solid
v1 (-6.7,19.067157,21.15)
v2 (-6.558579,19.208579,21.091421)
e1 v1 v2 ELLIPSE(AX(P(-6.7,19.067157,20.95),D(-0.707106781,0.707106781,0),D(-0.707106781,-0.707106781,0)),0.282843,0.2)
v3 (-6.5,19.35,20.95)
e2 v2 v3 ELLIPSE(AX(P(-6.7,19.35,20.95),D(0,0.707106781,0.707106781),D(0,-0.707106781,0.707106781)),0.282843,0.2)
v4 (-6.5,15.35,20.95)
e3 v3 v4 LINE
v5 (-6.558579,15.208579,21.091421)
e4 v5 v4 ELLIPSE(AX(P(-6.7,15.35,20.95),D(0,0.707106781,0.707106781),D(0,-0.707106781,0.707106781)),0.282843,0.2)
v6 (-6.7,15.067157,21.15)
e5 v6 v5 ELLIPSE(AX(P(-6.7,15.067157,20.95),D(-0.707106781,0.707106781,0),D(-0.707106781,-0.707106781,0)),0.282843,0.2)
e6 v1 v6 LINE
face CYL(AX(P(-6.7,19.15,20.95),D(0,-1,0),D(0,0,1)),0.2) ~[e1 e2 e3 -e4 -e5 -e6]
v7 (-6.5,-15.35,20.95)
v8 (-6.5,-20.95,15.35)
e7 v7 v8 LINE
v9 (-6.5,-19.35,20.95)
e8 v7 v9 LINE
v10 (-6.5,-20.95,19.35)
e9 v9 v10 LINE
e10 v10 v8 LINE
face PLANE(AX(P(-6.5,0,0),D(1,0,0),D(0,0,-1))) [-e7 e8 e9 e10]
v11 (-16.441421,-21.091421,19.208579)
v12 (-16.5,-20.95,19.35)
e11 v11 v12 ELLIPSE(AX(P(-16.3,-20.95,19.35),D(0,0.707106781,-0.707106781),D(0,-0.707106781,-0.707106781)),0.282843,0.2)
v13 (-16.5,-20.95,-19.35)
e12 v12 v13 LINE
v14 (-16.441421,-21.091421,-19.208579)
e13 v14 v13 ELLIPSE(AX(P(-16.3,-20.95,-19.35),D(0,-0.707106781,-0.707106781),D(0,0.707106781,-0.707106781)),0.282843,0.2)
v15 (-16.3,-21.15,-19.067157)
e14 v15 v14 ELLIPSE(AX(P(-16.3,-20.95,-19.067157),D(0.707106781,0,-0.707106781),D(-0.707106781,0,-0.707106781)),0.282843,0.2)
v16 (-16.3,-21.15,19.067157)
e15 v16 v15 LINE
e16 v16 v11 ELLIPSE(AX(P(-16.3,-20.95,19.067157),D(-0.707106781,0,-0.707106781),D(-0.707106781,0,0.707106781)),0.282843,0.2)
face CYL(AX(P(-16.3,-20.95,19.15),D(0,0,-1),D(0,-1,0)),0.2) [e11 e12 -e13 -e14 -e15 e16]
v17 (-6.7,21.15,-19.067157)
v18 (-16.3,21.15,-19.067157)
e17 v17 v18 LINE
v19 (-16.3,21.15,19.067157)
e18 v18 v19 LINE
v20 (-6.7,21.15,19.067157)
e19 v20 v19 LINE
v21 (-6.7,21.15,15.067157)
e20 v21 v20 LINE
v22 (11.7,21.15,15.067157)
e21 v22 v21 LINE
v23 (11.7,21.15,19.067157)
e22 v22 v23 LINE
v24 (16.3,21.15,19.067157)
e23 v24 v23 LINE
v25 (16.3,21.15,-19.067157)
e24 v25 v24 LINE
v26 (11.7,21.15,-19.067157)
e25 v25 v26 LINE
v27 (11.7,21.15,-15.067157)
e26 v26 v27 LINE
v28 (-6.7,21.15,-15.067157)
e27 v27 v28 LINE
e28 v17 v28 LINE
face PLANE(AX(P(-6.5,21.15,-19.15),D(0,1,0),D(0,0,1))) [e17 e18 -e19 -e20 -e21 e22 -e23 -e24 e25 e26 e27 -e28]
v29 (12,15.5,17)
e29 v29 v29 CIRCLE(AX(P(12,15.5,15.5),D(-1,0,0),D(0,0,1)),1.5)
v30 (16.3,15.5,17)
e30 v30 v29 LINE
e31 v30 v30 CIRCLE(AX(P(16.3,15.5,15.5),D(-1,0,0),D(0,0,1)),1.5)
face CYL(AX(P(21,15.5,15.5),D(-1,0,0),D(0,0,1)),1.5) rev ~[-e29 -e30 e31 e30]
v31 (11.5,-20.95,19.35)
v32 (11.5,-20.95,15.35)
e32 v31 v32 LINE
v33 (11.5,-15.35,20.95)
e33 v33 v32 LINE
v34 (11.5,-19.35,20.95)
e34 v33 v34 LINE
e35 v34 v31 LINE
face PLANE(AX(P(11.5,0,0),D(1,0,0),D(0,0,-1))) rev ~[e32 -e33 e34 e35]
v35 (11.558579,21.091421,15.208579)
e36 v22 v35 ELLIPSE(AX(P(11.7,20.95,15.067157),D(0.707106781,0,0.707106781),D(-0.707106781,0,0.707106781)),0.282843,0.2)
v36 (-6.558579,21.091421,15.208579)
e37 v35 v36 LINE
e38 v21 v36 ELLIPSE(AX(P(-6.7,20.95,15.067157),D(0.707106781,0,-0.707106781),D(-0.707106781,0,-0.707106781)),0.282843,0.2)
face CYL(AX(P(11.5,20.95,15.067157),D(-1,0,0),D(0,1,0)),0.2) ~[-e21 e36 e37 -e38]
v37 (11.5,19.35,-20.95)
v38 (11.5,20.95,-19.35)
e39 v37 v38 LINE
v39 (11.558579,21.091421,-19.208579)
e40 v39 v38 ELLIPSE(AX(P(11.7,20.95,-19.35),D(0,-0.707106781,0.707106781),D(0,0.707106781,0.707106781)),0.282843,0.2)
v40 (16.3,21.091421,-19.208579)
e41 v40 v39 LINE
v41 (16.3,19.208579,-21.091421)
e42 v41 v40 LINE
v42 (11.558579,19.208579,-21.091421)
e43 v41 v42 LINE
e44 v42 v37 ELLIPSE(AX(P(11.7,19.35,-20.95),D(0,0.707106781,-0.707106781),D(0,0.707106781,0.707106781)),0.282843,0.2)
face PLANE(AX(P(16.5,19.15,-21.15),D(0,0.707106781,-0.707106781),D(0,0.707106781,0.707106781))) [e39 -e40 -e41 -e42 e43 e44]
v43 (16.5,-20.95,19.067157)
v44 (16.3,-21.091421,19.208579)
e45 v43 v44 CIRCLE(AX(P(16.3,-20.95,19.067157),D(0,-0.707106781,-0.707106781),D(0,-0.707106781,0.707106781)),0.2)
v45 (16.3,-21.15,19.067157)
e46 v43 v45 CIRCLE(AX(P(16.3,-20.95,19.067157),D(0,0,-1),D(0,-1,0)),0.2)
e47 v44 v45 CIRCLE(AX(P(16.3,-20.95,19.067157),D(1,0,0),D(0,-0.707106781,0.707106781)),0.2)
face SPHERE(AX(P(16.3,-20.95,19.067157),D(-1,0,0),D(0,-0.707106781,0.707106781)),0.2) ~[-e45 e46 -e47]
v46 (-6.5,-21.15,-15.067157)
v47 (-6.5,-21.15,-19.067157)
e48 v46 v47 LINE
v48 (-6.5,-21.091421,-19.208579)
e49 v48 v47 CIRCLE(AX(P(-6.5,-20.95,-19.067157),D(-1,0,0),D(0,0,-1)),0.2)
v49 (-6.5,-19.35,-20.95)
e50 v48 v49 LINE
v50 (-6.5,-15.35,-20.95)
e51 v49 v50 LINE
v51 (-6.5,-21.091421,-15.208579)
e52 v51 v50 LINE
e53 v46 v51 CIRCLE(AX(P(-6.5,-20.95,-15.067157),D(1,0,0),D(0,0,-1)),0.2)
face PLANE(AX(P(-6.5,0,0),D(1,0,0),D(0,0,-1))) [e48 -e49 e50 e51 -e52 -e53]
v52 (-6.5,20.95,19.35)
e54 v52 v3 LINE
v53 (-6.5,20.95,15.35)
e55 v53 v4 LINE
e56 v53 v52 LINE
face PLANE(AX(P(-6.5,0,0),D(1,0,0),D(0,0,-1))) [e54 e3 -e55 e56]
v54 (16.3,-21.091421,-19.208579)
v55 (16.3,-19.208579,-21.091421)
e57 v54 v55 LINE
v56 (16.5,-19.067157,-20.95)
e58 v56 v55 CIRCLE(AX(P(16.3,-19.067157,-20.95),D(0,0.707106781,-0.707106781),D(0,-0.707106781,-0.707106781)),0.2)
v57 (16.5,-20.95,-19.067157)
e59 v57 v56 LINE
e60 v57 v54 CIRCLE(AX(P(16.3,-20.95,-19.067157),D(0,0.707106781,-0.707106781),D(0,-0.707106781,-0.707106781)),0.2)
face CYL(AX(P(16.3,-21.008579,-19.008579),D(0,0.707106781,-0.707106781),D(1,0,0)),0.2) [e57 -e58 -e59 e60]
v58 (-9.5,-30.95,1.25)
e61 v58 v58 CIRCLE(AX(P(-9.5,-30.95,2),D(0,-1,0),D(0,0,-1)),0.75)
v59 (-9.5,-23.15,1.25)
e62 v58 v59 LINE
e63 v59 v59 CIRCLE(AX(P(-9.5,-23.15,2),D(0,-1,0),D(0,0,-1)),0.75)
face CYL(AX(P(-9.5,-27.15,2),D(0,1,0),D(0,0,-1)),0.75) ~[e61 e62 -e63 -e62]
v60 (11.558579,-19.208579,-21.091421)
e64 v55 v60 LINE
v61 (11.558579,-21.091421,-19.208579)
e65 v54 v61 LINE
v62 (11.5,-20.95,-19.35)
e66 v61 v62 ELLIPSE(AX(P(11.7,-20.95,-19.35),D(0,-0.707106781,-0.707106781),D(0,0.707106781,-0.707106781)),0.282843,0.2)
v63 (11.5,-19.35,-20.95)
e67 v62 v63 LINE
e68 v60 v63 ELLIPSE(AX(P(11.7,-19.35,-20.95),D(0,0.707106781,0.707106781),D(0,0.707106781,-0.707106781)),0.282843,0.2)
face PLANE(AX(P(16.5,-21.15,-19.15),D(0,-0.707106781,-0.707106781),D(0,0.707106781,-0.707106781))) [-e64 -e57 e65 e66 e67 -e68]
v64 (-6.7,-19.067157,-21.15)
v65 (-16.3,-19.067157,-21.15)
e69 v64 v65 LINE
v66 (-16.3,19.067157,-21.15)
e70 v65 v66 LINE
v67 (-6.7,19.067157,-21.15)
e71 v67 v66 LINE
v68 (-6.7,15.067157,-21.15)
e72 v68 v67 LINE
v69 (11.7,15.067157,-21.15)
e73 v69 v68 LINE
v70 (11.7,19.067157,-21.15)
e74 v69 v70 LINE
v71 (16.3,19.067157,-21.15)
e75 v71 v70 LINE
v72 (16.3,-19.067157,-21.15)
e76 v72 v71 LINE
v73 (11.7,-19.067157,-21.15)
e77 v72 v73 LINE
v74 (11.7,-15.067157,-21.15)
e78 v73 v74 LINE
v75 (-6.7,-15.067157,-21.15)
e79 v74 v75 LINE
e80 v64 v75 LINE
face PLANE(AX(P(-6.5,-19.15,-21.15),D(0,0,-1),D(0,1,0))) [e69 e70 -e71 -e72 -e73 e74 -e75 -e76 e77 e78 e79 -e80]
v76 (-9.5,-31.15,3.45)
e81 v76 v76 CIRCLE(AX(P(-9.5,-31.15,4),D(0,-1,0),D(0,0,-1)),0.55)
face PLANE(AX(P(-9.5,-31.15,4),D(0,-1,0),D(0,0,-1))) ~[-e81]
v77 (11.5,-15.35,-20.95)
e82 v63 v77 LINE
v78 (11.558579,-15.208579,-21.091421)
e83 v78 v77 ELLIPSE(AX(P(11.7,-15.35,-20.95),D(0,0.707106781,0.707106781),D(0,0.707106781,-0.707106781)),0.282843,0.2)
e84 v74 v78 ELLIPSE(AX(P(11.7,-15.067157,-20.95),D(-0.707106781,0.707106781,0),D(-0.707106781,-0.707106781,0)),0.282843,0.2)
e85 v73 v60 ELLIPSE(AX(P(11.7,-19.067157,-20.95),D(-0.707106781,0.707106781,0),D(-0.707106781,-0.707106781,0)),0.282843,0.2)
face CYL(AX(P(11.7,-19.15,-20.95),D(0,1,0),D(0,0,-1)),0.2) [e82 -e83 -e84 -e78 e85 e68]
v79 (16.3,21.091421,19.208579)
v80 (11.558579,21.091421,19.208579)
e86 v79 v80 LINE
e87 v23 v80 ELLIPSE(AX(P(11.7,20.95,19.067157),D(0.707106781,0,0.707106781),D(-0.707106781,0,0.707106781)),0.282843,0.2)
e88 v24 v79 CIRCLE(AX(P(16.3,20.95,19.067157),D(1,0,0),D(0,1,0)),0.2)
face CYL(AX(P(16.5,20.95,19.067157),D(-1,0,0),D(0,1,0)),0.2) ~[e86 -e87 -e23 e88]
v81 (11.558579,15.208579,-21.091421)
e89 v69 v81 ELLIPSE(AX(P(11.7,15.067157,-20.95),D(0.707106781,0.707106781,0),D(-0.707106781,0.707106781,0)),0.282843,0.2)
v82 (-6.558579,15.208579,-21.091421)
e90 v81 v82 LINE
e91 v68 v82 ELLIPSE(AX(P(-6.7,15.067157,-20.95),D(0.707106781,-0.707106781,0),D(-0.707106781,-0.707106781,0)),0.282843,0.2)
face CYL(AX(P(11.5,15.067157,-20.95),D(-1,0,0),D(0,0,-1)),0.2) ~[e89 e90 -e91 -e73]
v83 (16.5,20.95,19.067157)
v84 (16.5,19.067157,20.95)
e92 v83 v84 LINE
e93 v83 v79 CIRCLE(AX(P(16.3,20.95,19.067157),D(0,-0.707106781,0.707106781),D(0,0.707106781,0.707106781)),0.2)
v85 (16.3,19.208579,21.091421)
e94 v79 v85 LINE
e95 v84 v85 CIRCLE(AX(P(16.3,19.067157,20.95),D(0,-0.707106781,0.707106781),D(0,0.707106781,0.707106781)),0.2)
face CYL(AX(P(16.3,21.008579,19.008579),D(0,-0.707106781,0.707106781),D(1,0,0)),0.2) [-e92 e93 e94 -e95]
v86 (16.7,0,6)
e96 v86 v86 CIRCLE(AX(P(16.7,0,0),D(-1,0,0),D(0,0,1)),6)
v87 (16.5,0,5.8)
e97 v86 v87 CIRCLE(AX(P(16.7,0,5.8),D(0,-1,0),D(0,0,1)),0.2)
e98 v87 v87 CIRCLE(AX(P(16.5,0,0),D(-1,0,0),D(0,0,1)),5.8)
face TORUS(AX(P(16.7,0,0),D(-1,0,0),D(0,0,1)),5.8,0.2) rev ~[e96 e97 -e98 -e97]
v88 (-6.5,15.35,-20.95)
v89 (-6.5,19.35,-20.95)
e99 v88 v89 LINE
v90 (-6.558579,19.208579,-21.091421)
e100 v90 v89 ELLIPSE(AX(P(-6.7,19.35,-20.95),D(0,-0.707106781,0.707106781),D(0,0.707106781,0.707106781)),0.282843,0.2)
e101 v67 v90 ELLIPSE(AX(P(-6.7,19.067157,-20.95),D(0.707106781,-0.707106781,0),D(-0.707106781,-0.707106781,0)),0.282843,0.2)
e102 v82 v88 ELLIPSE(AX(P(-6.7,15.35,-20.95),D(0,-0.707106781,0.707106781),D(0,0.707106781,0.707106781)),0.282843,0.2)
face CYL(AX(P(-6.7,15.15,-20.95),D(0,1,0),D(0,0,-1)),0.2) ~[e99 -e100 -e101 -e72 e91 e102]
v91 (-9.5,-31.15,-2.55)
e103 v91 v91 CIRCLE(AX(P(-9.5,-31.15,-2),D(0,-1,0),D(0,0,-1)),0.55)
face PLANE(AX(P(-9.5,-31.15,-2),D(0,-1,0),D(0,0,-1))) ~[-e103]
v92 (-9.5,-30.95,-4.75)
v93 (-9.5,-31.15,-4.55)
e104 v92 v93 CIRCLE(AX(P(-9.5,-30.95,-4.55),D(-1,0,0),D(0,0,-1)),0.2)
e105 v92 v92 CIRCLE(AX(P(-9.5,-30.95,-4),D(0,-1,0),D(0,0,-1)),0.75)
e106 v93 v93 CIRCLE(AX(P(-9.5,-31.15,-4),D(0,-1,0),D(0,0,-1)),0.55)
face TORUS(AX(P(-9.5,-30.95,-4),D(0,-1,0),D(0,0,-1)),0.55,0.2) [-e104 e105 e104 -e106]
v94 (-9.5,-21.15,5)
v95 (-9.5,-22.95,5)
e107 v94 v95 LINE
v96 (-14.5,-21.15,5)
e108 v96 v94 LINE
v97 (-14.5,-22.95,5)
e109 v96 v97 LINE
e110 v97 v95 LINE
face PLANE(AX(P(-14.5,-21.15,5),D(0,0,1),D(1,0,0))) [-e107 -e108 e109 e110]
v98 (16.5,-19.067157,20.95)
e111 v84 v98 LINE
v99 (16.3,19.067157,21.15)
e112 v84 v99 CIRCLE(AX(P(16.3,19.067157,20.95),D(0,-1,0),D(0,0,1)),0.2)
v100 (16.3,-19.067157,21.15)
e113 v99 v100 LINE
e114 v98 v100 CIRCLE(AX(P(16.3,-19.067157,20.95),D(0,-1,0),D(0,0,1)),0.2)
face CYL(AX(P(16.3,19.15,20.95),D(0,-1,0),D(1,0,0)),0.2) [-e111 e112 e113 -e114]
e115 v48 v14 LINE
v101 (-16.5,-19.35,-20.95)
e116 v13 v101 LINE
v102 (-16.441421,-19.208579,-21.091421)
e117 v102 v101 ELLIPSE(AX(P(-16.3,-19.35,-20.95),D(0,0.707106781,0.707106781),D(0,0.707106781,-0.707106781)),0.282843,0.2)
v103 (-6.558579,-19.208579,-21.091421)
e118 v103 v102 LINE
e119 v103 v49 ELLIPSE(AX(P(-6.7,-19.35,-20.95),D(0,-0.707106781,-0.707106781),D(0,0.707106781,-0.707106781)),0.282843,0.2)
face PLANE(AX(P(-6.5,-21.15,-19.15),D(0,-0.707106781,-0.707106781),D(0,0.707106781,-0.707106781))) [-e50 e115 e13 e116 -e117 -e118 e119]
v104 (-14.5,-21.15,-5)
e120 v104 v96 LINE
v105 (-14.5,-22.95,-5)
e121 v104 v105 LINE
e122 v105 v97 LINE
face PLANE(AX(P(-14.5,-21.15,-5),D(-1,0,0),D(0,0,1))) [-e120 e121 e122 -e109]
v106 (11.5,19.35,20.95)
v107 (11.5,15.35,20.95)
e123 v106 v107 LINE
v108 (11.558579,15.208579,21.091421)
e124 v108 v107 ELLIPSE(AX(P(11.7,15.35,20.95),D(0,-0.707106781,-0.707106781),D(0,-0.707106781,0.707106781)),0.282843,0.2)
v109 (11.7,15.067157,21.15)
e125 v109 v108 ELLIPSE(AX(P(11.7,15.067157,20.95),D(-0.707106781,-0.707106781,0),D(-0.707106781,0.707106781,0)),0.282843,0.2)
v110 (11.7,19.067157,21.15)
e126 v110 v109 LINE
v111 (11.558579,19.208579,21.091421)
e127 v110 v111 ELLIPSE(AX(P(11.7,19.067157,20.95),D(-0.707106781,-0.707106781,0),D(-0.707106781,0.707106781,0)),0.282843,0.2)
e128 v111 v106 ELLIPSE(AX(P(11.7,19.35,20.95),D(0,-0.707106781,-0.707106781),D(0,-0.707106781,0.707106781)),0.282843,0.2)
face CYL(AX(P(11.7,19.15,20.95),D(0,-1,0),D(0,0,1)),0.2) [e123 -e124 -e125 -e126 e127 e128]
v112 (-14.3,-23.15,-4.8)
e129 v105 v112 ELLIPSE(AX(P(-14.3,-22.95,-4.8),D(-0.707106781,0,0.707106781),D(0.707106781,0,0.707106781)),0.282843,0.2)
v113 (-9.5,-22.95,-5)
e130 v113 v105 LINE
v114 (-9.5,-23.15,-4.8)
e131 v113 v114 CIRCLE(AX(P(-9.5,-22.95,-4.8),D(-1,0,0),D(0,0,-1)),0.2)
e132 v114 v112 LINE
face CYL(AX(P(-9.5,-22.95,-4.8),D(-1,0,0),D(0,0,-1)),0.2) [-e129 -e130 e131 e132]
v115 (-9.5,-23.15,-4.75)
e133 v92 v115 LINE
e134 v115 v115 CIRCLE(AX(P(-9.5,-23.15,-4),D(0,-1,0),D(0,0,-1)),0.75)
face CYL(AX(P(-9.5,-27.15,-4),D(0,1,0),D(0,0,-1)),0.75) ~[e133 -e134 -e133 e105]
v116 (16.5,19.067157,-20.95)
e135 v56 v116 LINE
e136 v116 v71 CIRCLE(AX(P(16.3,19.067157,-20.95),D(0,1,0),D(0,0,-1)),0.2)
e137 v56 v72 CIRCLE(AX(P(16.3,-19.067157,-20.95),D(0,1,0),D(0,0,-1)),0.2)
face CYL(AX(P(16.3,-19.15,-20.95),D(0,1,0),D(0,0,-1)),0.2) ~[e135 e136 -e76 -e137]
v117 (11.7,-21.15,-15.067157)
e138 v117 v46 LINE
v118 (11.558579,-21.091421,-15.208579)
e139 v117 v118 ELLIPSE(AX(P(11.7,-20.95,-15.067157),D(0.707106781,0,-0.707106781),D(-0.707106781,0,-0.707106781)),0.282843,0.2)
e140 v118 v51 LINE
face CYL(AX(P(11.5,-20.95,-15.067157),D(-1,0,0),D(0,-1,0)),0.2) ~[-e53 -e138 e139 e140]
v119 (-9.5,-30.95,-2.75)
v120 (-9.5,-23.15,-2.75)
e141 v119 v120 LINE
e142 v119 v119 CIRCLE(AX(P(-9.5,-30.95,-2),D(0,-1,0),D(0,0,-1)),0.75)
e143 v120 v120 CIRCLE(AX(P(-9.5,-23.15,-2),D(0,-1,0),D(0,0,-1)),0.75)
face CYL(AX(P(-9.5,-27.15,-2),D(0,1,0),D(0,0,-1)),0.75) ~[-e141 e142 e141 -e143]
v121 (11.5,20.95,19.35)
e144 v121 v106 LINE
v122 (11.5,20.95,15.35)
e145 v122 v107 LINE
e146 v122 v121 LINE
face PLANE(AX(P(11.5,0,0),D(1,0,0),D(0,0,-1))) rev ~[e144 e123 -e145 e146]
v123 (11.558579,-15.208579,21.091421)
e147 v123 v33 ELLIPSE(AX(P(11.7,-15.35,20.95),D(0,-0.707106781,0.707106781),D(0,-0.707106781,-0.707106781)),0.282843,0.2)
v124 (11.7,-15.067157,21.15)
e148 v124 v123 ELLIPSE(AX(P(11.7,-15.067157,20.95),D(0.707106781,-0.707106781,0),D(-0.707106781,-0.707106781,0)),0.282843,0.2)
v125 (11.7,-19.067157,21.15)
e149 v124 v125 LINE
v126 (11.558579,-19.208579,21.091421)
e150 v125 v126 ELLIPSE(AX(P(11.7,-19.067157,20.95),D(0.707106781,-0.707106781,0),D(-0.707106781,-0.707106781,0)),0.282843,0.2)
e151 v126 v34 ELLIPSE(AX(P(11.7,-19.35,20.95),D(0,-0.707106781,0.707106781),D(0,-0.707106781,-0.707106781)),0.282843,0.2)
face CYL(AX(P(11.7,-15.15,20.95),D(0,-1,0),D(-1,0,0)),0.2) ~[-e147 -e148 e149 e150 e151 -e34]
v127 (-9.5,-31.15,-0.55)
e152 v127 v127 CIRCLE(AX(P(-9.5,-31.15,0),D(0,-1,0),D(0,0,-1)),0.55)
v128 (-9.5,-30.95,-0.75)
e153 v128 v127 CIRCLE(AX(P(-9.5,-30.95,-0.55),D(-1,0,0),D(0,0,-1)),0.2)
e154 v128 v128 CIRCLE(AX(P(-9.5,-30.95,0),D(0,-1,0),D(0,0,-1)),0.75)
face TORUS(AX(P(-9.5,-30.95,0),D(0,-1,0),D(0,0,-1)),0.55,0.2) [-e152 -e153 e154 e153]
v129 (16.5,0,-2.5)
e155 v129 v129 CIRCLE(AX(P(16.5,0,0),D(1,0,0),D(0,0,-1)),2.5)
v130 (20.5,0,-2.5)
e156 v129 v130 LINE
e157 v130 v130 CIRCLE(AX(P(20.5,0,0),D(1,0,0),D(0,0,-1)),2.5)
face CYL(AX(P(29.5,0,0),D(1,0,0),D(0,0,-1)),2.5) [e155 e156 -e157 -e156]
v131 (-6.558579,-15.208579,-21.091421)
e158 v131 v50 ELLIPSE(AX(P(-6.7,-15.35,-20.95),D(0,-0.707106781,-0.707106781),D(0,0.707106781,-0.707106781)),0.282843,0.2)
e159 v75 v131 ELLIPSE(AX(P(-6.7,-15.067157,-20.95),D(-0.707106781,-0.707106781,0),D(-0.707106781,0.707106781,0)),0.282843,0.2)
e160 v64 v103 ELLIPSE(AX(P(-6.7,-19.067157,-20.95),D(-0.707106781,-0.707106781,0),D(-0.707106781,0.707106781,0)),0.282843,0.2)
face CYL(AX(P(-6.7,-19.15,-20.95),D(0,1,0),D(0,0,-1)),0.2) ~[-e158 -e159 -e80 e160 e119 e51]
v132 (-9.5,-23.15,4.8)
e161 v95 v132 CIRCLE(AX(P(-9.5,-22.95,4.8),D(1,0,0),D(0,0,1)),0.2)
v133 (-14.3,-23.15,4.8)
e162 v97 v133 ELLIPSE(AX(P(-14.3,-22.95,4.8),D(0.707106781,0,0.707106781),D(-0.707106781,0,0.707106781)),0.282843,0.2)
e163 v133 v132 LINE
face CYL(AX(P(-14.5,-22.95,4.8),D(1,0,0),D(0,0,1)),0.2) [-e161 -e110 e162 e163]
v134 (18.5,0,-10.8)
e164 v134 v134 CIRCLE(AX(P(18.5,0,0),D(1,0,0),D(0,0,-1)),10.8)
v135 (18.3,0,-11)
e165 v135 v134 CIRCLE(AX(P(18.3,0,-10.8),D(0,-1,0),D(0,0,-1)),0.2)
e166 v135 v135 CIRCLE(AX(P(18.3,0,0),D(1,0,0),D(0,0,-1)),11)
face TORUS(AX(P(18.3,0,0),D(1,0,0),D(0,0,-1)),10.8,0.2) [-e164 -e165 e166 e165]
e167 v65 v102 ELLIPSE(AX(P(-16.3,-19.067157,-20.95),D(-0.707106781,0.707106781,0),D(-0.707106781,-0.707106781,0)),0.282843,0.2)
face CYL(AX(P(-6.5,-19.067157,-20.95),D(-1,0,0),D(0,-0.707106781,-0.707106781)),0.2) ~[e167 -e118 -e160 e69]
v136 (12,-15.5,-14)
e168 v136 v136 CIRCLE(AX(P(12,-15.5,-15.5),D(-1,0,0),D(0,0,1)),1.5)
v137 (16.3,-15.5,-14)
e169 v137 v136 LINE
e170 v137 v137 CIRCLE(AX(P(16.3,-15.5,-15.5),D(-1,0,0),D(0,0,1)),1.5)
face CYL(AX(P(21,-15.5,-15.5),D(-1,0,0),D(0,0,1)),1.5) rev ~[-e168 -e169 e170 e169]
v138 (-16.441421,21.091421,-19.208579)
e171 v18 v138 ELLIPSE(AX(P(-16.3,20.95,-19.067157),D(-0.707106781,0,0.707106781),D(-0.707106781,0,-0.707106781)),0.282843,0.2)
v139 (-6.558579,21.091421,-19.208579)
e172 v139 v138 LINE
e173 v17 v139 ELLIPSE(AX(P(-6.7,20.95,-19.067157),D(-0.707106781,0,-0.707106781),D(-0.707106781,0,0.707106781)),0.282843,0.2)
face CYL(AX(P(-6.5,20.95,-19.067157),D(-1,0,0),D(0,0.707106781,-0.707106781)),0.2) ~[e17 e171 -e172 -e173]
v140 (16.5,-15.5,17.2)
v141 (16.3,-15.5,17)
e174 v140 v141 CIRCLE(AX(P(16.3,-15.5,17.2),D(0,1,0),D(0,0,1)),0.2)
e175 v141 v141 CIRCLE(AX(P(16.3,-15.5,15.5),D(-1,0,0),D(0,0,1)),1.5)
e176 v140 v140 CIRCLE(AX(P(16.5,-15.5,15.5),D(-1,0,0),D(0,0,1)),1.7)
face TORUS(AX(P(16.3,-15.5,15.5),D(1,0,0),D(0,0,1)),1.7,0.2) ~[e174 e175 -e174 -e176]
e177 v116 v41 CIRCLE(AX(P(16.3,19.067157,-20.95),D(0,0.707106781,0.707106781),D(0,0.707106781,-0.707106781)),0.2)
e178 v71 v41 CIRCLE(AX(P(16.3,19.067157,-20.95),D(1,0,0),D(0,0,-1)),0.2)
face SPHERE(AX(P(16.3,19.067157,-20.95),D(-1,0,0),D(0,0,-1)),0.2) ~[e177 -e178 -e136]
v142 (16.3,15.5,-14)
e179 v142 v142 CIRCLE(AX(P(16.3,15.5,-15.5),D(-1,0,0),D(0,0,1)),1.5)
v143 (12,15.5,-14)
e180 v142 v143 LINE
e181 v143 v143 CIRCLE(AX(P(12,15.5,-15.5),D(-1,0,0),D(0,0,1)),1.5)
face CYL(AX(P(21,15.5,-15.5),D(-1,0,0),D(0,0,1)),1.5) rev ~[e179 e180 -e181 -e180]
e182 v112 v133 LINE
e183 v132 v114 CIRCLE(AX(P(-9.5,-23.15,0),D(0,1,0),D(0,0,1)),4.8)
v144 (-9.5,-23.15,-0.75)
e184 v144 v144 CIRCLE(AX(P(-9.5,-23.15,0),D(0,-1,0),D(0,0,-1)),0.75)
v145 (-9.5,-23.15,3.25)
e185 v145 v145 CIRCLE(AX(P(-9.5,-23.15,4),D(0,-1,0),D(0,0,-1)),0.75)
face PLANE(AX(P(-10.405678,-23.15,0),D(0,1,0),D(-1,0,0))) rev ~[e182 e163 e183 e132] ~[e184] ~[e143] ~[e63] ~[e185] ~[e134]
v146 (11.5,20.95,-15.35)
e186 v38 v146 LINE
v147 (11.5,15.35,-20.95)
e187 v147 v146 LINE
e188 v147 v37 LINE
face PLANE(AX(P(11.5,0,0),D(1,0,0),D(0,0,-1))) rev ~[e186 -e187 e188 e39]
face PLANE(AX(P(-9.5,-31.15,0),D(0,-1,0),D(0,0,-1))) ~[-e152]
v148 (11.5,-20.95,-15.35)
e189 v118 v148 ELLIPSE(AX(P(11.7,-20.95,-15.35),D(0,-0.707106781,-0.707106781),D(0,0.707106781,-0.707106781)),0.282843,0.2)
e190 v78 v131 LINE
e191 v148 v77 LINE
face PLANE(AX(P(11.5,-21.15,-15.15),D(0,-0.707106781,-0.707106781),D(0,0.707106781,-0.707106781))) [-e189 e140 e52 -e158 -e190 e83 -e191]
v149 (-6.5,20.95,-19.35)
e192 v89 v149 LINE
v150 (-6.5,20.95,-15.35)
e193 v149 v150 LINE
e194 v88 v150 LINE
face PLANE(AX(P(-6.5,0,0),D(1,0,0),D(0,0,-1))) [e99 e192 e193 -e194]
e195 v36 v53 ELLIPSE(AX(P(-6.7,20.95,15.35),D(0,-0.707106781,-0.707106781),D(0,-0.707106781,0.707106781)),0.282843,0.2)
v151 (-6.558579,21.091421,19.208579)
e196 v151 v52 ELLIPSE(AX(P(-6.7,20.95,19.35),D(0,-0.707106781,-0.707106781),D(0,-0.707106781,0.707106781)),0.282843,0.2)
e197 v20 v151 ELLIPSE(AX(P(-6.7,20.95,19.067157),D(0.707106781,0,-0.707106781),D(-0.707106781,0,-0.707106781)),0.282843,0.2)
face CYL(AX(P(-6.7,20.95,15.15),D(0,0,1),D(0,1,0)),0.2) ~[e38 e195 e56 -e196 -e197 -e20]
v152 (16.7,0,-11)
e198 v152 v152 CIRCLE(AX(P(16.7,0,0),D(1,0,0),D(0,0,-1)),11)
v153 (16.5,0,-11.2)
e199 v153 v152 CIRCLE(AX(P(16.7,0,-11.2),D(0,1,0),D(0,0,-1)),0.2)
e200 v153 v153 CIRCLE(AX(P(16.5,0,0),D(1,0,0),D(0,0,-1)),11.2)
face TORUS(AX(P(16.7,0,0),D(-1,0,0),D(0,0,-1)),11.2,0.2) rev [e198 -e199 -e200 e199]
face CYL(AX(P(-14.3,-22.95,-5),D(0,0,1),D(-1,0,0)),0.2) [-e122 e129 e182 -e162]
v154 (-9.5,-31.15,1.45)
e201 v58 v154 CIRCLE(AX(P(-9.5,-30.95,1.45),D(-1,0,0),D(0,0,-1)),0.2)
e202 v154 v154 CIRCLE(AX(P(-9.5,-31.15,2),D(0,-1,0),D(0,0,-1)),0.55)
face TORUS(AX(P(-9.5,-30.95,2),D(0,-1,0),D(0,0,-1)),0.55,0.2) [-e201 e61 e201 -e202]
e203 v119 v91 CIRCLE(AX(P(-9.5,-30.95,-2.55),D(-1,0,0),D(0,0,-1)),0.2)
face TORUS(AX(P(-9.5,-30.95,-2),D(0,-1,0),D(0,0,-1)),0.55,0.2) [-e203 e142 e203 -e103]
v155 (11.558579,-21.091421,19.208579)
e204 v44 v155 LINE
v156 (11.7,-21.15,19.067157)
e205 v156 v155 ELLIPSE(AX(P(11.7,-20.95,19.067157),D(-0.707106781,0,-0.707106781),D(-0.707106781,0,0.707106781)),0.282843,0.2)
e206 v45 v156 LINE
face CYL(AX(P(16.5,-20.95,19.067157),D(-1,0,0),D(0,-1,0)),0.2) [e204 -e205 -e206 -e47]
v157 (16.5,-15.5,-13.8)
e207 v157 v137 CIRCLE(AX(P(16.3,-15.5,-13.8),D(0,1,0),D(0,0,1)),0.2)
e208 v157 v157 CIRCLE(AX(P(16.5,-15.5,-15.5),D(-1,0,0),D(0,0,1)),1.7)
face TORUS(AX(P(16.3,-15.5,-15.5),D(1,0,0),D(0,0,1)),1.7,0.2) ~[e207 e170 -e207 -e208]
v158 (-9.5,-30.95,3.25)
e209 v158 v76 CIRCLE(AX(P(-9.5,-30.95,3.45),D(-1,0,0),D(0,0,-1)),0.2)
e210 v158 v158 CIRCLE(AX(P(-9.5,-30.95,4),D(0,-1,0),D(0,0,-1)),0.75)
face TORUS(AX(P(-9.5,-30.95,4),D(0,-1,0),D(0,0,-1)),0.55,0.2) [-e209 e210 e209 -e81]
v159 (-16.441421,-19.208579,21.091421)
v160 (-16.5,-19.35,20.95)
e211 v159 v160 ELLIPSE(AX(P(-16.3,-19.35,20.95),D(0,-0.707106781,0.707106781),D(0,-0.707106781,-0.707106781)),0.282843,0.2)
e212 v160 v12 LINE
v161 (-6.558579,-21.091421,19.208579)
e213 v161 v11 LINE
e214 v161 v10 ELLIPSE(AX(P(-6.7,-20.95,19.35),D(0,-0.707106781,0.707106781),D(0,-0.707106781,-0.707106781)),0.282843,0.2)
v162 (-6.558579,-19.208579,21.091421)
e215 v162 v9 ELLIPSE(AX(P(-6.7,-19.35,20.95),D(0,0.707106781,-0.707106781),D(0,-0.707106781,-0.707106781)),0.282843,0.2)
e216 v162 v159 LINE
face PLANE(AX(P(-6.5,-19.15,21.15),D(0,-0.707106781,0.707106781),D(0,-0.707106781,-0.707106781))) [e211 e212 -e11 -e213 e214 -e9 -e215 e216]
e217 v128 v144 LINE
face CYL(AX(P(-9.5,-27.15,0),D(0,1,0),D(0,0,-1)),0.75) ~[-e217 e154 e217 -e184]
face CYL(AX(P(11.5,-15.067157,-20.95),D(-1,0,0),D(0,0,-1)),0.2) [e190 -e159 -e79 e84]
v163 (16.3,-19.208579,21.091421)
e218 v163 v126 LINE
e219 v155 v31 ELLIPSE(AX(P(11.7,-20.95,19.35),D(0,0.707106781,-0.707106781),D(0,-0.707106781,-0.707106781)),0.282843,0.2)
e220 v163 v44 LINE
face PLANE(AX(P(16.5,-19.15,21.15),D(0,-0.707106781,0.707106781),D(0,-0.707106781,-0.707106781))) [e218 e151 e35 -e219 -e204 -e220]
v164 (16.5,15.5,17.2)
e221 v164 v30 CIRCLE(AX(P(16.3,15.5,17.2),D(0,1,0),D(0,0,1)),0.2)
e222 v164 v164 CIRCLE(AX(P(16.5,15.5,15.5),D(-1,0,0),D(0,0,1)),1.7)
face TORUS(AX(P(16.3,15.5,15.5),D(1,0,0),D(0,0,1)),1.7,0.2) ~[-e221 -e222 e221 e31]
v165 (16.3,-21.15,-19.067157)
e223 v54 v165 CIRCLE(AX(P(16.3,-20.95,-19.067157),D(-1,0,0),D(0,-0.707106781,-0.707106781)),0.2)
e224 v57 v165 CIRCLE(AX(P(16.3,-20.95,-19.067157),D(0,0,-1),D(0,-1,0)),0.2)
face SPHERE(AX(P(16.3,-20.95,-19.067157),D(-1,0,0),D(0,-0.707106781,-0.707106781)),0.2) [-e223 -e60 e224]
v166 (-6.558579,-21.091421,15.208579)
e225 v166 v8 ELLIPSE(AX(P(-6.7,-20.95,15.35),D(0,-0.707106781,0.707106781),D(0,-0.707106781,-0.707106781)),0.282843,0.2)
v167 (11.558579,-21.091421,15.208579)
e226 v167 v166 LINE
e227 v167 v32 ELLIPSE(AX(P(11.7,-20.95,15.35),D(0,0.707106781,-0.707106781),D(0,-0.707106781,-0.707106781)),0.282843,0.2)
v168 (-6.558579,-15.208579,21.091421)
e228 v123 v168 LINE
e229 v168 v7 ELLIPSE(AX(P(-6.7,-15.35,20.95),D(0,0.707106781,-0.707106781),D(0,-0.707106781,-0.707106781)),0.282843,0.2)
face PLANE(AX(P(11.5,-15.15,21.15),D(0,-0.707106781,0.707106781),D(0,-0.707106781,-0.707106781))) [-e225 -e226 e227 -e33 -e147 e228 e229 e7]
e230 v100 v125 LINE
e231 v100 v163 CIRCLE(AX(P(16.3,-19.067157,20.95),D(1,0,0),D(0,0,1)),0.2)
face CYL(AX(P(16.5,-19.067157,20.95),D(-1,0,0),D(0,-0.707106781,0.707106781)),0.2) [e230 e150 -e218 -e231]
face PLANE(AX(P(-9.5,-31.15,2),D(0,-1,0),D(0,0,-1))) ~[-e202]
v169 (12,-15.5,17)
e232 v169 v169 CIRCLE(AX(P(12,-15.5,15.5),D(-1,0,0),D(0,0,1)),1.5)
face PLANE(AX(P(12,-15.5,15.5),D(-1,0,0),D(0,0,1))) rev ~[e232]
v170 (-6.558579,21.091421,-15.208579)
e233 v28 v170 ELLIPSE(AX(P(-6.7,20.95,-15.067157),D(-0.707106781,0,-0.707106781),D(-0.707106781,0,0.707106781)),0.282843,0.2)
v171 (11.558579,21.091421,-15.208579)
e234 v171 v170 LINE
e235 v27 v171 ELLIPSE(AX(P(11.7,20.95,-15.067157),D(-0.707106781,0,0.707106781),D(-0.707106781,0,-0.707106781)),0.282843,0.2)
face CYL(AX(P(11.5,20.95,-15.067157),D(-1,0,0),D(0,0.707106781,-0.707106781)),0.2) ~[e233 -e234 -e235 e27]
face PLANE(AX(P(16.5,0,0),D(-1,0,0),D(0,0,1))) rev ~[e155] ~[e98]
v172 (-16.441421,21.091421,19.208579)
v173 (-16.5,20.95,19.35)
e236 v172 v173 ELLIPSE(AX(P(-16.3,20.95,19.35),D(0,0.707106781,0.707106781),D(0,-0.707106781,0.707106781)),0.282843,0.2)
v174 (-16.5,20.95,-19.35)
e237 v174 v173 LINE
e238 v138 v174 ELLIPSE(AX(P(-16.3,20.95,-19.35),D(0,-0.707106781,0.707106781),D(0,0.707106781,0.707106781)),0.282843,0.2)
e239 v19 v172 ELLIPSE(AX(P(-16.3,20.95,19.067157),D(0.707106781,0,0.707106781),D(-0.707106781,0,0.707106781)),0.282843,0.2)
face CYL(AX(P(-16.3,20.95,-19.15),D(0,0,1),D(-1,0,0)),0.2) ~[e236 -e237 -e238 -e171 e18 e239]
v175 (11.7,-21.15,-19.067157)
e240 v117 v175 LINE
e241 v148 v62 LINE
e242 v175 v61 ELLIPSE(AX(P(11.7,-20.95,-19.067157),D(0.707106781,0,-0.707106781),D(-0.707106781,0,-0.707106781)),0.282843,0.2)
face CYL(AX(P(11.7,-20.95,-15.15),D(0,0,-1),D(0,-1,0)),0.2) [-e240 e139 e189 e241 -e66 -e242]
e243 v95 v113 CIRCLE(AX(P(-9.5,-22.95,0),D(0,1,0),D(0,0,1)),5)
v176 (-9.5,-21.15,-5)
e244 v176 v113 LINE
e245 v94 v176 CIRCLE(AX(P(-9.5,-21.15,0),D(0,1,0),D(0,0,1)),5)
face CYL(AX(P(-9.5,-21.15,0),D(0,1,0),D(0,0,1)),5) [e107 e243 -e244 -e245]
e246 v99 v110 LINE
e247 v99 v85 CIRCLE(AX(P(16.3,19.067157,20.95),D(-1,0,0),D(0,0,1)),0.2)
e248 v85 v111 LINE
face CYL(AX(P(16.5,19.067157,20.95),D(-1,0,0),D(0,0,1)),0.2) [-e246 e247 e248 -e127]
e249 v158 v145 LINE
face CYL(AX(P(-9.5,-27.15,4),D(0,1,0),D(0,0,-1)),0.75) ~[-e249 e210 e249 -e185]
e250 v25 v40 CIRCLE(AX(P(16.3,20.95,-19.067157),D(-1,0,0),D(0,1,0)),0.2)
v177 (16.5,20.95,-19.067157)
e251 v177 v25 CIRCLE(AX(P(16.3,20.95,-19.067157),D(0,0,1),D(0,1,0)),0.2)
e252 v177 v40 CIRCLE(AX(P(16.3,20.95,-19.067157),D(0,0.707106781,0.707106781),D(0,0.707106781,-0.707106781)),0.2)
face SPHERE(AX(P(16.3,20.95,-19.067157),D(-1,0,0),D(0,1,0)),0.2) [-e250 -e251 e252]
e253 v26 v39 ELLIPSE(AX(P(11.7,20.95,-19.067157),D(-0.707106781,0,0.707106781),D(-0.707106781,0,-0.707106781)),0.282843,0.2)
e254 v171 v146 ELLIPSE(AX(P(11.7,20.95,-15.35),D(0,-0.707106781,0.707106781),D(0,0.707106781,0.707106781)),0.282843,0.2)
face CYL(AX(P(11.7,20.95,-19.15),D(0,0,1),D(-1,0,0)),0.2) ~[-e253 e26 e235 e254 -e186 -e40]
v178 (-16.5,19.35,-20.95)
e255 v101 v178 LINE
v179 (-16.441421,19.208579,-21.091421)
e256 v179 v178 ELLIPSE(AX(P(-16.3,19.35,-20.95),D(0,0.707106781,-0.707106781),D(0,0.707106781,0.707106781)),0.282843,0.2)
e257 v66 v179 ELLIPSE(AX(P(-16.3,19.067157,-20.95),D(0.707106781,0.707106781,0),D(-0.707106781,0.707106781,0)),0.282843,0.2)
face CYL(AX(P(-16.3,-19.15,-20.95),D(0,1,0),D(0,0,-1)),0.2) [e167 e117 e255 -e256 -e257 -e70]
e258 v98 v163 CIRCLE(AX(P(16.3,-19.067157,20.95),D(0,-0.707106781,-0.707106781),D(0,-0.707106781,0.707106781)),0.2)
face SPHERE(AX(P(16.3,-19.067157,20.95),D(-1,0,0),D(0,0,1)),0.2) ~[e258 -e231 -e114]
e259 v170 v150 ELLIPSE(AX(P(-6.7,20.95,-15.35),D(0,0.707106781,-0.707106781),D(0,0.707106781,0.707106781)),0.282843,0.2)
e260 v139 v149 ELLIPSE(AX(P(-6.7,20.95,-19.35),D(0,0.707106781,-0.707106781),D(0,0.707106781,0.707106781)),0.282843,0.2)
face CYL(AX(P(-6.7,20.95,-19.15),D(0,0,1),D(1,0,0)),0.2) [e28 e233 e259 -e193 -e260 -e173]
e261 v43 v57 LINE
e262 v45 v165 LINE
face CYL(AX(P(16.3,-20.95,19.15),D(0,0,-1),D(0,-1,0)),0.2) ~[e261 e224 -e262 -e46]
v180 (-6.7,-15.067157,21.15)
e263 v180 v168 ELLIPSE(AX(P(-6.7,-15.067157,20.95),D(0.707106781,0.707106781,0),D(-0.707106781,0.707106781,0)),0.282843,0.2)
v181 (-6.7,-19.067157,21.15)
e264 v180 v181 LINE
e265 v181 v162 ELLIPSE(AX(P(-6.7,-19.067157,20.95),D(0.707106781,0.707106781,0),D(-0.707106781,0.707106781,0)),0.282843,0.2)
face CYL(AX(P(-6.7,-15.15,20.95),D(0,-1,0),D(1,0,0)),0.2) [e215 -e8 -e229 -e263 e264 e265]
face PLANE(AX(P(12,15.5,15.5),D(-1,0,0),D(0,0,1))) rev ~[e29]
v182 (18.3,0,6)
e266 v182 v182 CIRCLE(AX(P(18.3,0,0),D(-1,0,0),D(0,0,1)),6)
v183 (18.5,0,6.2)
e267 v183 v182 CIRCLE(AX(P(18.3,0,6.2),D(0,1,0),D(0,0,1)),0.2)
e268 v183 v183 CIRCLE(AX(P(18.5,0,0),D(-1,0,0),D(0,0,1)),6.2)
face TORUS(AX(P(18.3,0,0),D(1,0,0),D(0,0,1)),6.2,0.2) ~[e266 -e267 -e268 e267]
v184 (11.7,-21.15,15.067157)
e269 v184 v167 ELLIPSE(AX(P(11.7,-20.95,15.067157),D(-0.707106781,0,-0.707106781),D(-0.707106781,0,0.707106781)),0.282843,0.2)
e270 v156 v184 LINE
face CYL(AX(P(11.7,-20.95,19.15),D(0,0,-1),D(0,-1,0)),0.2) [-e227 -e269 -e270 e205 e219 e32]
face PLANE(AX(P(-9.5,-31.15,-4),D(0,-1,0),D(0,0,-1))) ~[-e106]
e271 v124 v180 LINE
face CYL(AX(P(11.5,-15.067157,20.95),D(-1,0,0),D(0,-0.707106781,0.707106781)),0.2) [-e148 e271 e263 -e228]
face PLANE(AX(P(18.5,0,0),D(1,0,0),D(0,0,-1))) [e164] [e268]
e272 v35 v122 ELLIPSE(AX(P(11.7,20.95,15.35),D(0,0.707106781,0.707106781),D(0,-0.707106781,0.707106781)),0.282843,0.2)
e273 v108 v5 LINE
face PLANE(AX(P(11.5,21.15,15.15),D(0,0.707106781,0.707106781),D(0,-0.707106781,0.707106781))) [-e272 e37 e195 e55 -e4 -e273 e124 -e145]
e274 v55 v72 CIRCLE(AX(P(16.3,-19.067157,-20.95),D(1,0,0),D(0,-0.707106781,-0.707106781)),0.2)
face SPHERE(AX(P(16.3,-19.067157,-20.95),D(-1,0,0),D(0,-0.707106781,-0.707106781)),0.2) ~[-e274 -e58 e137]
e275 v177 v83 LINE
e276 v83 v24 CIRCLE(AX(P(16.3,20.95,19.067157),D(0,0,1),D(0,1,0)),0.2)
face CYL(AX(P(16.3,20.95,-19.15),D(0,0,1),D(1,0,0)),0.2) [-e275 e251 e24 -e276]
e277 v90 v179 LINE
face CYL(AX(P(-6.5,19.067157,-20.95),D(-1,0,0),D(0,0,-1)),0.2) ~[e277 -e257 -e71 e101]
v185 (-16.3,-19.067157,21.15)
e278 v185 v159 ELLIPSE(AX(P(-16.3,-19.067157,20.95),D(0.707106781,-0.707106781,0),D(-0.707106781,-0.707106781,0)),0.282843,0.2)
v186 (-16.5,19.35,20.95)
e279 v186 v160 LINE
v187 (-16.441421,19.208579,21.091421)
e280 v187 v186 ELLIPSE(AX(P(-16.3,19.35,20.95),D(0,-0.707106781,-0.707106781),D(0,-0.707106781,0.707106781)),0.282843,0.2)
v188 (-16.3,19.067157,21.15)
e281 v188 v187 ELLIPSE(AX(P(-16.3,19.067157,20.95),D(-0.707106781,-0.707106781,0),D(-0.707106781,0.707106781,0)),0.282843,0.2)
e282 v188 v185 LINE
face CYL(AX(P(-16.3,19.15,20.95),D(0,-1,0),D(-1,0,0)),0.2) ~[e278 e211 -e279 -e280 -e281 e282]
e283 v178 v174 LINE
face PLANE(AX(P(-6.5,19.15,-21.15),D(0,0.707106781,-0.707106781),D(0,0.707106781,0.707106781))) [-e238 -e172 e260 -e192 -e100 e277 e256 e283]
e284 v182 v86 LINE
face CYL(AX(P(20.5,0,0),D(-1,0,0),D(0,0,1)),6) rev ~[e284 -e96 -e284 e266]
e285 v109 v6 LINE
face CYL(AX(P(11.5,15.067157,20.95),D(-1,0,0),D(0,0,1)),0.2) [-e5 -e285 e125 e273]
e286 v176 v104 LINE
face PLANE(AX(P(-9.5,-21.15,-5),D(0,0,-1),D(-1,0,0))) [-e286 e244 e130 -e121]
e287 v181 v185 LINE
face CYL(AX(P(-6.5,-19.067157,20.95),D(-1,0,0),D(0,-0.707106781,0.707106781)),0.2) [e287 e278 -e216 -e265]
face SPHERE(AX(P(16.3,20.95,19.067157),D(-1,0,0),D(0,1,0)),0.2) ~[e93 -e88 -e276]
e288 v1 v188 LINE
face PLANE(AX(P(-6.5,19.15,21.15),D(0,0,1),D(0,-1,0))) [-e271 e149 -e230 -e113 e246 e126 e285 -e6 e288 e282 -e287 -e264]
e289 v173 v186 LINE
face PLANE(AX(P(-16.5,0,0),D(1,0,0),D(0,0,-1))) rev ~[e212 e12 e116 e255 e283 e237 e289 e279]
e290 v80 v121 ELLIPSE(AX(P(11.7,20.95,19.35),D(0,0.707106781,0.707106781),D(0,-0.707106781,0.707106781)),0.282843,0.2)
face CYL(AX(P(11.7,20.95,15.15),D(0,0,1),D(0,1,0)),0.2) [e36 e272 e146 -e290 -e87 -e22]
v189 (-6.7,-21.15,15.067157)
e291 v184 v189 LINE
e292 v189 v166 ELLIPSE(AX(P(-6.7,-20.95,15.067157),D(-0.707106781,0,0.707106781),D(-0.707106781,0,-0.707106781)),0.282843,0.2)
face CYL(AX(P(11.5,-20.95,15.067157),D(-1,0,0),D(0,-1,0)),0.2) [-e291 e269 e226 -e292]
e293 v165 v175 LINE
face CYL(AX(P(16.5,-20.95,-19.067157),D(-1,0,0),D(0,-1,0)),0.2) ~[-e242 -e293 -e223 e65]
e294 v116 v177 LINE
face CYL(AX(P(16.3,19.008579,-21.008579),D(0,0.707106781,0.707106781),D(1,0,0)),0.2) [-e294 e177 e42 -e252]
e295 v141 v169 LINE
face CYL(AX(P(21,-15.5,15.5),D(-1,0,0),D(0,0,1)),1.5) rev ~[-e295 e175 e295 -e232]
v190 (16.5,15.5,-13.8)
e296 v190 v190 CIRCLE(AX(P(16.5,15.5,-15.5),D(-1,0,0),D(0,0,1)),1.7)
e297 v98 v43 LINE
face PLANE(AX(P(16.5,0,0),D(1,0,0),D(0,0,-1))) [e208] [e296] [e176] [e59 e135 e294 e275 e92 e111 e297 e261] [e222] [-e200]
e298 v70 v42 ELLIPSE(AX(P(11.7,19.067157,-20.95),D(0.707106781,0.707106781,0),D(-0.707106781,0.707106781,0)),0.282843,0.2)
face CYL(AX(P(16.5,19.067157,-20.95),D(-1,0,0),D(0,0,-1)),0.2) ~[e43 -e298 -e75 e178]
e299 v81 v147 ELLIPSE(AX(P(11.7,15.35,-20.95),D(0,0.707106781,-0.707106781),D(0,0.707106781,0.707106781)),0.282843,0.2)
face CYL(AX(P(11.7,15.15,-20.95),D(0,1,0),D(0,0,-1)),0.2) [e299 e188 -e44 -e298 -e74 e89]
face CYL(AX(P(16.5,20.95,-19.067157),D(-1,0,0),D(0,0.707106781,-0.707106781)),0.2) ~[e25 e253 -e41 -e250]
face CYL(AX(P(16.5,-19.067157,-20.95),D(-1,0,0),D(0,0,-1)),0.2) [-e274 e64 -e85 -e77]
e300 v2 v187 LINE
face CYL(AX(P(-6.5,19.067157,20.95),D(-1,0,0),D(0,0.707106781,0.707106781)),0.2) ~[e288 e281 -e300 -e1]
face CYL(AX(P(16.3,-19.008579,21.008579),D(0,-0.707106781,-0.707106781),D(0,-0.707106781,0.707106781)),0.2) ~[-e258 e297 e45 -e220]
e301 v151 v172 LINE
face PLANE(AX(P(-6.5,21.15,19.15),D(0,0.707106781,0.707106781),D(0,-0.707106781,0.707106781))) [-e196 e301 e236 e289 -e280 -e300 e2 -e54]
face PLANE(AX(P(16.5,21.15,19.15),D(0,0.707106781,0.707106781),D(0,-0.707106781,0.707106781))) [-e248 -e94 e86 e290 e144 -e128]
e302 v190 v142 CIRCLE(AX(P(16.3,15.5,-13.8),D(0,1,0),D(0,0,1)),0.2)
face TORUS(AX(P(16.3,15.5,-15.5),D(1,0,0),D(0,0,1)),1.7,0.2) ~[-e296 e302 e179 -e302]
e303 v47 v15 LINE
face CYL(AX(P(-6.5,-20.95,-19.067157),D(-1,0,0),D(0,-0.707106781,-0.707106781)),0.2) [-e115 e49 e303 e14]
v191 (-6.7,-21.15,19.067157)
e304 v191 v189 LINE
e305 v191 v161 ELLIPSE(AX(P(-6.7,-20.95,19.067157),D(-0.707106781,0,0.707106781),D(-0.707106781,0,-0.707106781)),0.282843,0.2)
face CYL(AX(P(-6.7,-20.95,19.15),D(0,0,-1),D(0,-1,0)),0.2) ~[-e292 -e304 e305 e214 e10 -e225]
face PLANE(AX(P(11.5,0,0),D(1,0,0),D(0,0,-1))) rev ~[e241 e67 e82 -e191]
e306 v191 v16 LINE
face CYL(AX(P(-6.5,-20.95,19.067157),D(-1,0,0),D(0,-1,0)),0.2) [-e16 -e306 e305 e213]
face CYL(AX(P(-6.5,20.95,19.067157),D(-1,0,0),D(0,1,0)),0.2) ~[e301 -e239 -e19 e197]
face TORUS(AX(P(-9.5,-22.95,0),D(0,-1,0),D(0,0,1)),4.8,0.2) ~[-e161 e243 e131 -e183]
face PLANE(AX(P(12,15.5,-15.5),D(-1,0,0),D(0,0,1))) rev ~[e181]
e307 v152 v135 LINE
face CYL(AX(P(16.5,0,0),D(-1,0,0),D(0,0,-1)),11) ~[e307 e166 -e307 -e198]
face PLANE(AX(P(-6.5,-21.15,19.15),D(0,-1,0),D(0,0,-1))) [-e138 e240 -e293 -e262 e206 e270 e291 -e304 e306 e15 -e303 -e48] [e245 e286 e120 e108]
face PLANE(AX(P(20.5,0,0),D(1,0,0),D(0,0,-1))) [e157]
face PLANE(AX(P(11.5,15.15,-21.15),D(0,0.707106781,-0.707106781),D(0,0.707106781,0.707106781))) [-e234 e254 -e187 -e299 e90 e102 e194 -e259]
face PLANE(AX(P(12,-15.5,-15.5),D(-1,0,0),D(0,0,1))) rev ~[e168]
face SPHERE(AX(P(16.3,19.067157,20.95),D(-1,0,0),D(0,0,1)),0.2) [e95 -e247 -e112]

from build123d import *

# Parameters (mm, degrees)
BOSS_EXTRUDE1_DEPTH            = 5
BOSS_EXTRUDE2_DEPTH            = 18
BOSS_EXTRUDE3_DEPTH            = 10
BOSS_EXTRUDE4_DEPTH            = 2
SKETCH5_R                      = 11
BOSS_EXTRUDE5_DEPTH            = 2
F_12_0_12_DIAMETER_HOLE1_D     = 12.000000009
F_12_0_12_DIAMETER_HOLE1_DEPTH = 2
SKETCH8_W                      = 0.75
SKETCH8_H                      = 8
SKETCH9_W                      = 0.75
SKETCH9_H                      = 8
SKETCH10_W                     = 0.75
SKETCH10_H                     = 8
SKETCH11_W                     = 0.75
SKETCH11_H                     = 8
SKETCH12_W                     = 0.75
SKETCH12_H                     = 8
SKETCH13_W                     = 26
SKETCH13_H                     = 2.5
F_3_0_3_DIAMETER_HOLE1_D       = 2.999999994
F_3_0_3_DIAMETER_HOLE1_DEPTH   = 4.5
FILLET1_R                      = 0.2
SKETCH16_R                     = 3.097425191
CUT_EXTRUDE1_DEPTH             = 22


with BuildPart() as part:
    # Sketch1 → Boss-Extrude1 (new body)
    with BuildSketch(Plane(origin=(16.5, 0, 0), x_dir=(0, 0, -1), z_dir=(1, 0, 0))):
        Polygon((-21.15, 19.15), (-21.15, -19.15), (-19.15, -21.15), (19.15, -21.15), (21.15, -19.15), (21.15, 19.15), (19.15, 21.15), (-19.15, 21.15), align=None)
    extrude(amount=-BOSS_EXTRUDE1_DEPTH)

    # Sketch2 → Boss-Extrude2 (add)
    with BuildSketch(Plane.ZY.offset(-11.5)):
        Polygon((-15.15, 21.15), (15.15, 21.15), (21.15, 15.15), (21.15, -15.15), (15.15, -21.15), (-15.15, -21.15), (-21.15, -15.15), (-21.15, 15.15), align=None)
    extrude(amount=BOSS_EXTRUDE2_DEPTH)

    # Sketch3 → Boss-Extrude3 (add)
    with BuildSketch(Plane.ZY.offset(6.5)):
        Polygon((-19.15, -21.15), (-21.15, -19.15), (-21.15, 19.15), (-19.15, 21.15), (19.15, 21.15), (21.15, 19.15), (21.15, -19.15), (19.15, -21.15), align=None)
    extrude(amount=BOSS_EXTRUDE3_DEPTH)

    # Sketch4 → Boss-Extrude4 (add)
    with BuildSketch(Plane.XZ.offset(21.15)):
        with BuildLine():
            Line((-9.5, -5), (-14.5, -5))
            Line((-14.5, -5), (-14.5, 5))
            Line((-14.5, 5), (-9.5, 5))
            ThreePointArc((-9.5, 5), (-4.5, 0), (-9.5, -5))
        make_face()
    extrude(amount=BOSS_EXTRUDE4_DEPTH)

    # Sketch5 → Boss-Extrude5 (add)
    with BuildSketch(Plane(origin=(16.5, 0, 0), x_dir=(0, 0, -1), z_dir=(1, 0, 0))):
        Circle(SKETCH5_R)
    extrude(amount=BOSS_EXTRUDE5_DEPTH)

    # Ø12.0 (12) Diameter Hole1
    with Locations(Plane(origin=(18.5, 0, 0), x_dir=(0, 0, -1), z_dir=(1, 0, 0))):
        with Locations((0, 0)):
            Hole(F_12_0_12_DIAMETER_HOLE1_D / 2, depth=F_12_0_12_DIAMETER_HOLE1_DEPTH)

    # Sketch8 → Revolve1 (revolve)
    with BuildSketch(Plane.XY.offset(-4), mode=Mode.PRIVATE) as revolve1_sk:
        with Locations((-9.125, -27.15)):
            Rectangle(SKETCH8_W, SKETCH8_H)
    revolve(revolve1_sk.sketch.rotate(Axis((-9.5, -23.15, -4), (0, -1, 0)), 270), axis=Axis((-9.5, -23.15, -4), (0, -1, 0)))

    # Sketch9 → Revolve2 (revolve)
    with BuildSketch(Plane.XY.offset(-2), mode=Mode.PRIVATE) as revolve2_sk:
        with Locations((-9.125, -27.15)):
            Rectangle(SKETCH9_W, SKETCH9_H)
    revolve(revolve2_sk.sketch.rotate(Axis((-9.5, -23.15, -2), (0, -1, 0)), 270), axis=Axis((-9.5, -23.15, -2), (0, -1, 0)))

    # Sketch10 → Revolve3 (revolve)
    with BuildSketch(Plane.XY.offset(4), mode=Mode.PRIVATE) as revolve3_sk:
        with Locations((-9.125, -27.15)):
            Rectangle(SKETCH10_W, SKETCH10_H)
    revolve(revolve3_sk.sketch.rotate(Axis((-9.5, -23.15, 4), (0, -1, 0)), 270), axis=Axis((-9.5, -23.15, 4), (0, -1, 0)))

    # Sketch11 → Revolve4 (revolve)
    with BuildSketch(Plane.XY.offset(2), mode=Mode.PRIVATE) as revolve4_sk:
        with Locations((-9.125, -27.15)):
            Rectangle(SKETCH11_W, SKETCH11_H)
    revolve(revolve4_sk.sketch.rotate(Axis((-9.5, -23.15, 2), (0, -1, 0)), 270), axis=Axis((-9.5, -23.15, 2), (0, -1, 0)))

    # Sketch12 → Revolve5 (revolve)
    with BuildSketch(Plane.XY, mode=Mode.PRIVATE) as revolve5_sk:
        with Locations((-9.125, -27.15)):
            Rectangle(SKETCH12_W, SKETCH12_H)
    revolve(revolve5_sk.sketch.rotate(Axis((-9.5, -23.15, 0), (0, -1, 0)), 270), axis=Axis((-9.5, -23.15, 0), (0, -1, 0)))

    # Sketch13 → Revolve6 (revolve)
    with BuildSketch(Plane.XY, mode=Mode.PRIVATE) as revolve6_sk:
        with Locations((29.5, 1.25)):
            Rectangle(SKETCH13_W, SKETCH13_H)
    revolve(revolve6_sk.sketch.rotate(Axis((16.5, 0, 0), (1, 0, 0)), 270), axis=Axis((16.5, 0, 0), (1, 0, 0)))

    # Ø3.0 (3) Diameter Hole1
    with Locations(Plane(origin=(16.5, 0, 0), x_dir=(0, 0, -1), z_dir=(1, 0, 0))):
        with Locations((-15.5, 15.5), (15.5, -15.5), (15.5, 15.5), (-15.5, -15.5)):
            Hole(F_3_0_3_DIAMETER_HOLE1_D / 2, depth=F_3_0_3_DIAMETER_HOLE1_DEPTH)

    # Fillet1
    fillet1_edges = [part.edges().sort_by_distance(p)[0] for p in [
        (-16.5, 21.15, 0),
        (-11.5, 21.15, -19.15),
        (-11.5, 21.15, 19.15),
        (-6.5, 21.15, -17.15),
        (-11.5, 19.15, -21.15),
        (-16.5, 0, -21.15),
        (-16.5, 0, 21.15),
        (-6.5, 21.15, 17.15),
        (-11.5, 19.15, 21.15),
        (2.5, 21.15, -15.15),
        (-6.5, 17.15, -21.15),
        (-11.5, -19.15, -21.15),
        (-11.5, -19.15, 21.15),
        (2.5, 21.15, 15.15),
        (-6.5, 17.15, 21.15),
        (11.5, 21.15, -17.15),
        (2.5, 15.15, -21.15),
        (-6.5, -17.15, -21.15),
        (-6.5, -17.15, 21.15),
        (11.5, 21.15, 17.15),
        (2.5, 15.15, 21.15),
        (14, 21.15, -19.15),
        (11.5, 17.15, -21.15),
        (2.5, -15.15, -21.15),
        (2.5, -15.15, 21.15),
        (14, 21.15, 19.15),
        (16.5, 21.15, 0),
        (11.5, 17.15, 21.15),
        (2.5, -21.15, -15.15),
        (16.5, 20.15, -20.15),
        (14, 19.15, -21.15),
        (11.5, -17.15, -21.15),
        (11.5, -17.15, 21.15),
        (16.5, 20.15, 20.15),
        (14, 19.15, 21.15),
        (11.5, -21.15, -17.15),
        (16.5, 0, -21.15),
        (14, -19.15, -21.15),
        (14, -19.15, 21.15),
        (16.5, 0, 21.15),
        (14, -21.15, -19.15),
        (16.5, -20.15, -20.15),
        (16.5, -20.15, 20.15),
        (16.5, -21.15, 0),
        (14, -21.15, 19.15),
        (11.5, -21.15, 17.15),
        (2.5, -21.15, 15.15),
        (-6.5, -21.15, 17.15),
        (-11.5, -21.15, 19.15),
        (-16.5, -21.15, 0),
        (-11.5, -21.15, -19.15),
        (16.5, 0, -6.000000005),
        (18.5, 0, -6.000000005),
        (18.5, 0, 11),
        (-9.5, -31.15, 0.75),
        (-9.5, -31.15, 2.75),
        (-9.5, -31.15, 4.75),
        (-9.5, -31.15, -1.25),
        (-9.5, -31.15, -3.25),
        (16.5, 0, 11),
        (16.5, 15.5, 14.000000003),
        (16.5, -15.5, -16.999999997),
        (16.5, 15.5, -16.999999997),
        (16.5, -15.5, 14.000000003),
        (42.5, 0, 2.5),
        (-14.5, -23.15, 0),
        (-12, -23.15, 5),
        (-12, -23.15, -5),
        (-4.5, -23.15, 0),
    ]]
    fillet(fillet1_edges, radius=FILLET1_R)

    # Sketch16 → Cut-Extrude1 (cut)
    with BuildSketch(Plane(origin=(42.5, 0, 0), x_dir=(0, 0, -1), z_dir=(1, 0, 0))):
        Circle(SKETCH16_R)
    extrude(amount=-CUT_EXTRUDE1_DEPTH, mode=Mode.SUBTRACT)


solid = part.part
